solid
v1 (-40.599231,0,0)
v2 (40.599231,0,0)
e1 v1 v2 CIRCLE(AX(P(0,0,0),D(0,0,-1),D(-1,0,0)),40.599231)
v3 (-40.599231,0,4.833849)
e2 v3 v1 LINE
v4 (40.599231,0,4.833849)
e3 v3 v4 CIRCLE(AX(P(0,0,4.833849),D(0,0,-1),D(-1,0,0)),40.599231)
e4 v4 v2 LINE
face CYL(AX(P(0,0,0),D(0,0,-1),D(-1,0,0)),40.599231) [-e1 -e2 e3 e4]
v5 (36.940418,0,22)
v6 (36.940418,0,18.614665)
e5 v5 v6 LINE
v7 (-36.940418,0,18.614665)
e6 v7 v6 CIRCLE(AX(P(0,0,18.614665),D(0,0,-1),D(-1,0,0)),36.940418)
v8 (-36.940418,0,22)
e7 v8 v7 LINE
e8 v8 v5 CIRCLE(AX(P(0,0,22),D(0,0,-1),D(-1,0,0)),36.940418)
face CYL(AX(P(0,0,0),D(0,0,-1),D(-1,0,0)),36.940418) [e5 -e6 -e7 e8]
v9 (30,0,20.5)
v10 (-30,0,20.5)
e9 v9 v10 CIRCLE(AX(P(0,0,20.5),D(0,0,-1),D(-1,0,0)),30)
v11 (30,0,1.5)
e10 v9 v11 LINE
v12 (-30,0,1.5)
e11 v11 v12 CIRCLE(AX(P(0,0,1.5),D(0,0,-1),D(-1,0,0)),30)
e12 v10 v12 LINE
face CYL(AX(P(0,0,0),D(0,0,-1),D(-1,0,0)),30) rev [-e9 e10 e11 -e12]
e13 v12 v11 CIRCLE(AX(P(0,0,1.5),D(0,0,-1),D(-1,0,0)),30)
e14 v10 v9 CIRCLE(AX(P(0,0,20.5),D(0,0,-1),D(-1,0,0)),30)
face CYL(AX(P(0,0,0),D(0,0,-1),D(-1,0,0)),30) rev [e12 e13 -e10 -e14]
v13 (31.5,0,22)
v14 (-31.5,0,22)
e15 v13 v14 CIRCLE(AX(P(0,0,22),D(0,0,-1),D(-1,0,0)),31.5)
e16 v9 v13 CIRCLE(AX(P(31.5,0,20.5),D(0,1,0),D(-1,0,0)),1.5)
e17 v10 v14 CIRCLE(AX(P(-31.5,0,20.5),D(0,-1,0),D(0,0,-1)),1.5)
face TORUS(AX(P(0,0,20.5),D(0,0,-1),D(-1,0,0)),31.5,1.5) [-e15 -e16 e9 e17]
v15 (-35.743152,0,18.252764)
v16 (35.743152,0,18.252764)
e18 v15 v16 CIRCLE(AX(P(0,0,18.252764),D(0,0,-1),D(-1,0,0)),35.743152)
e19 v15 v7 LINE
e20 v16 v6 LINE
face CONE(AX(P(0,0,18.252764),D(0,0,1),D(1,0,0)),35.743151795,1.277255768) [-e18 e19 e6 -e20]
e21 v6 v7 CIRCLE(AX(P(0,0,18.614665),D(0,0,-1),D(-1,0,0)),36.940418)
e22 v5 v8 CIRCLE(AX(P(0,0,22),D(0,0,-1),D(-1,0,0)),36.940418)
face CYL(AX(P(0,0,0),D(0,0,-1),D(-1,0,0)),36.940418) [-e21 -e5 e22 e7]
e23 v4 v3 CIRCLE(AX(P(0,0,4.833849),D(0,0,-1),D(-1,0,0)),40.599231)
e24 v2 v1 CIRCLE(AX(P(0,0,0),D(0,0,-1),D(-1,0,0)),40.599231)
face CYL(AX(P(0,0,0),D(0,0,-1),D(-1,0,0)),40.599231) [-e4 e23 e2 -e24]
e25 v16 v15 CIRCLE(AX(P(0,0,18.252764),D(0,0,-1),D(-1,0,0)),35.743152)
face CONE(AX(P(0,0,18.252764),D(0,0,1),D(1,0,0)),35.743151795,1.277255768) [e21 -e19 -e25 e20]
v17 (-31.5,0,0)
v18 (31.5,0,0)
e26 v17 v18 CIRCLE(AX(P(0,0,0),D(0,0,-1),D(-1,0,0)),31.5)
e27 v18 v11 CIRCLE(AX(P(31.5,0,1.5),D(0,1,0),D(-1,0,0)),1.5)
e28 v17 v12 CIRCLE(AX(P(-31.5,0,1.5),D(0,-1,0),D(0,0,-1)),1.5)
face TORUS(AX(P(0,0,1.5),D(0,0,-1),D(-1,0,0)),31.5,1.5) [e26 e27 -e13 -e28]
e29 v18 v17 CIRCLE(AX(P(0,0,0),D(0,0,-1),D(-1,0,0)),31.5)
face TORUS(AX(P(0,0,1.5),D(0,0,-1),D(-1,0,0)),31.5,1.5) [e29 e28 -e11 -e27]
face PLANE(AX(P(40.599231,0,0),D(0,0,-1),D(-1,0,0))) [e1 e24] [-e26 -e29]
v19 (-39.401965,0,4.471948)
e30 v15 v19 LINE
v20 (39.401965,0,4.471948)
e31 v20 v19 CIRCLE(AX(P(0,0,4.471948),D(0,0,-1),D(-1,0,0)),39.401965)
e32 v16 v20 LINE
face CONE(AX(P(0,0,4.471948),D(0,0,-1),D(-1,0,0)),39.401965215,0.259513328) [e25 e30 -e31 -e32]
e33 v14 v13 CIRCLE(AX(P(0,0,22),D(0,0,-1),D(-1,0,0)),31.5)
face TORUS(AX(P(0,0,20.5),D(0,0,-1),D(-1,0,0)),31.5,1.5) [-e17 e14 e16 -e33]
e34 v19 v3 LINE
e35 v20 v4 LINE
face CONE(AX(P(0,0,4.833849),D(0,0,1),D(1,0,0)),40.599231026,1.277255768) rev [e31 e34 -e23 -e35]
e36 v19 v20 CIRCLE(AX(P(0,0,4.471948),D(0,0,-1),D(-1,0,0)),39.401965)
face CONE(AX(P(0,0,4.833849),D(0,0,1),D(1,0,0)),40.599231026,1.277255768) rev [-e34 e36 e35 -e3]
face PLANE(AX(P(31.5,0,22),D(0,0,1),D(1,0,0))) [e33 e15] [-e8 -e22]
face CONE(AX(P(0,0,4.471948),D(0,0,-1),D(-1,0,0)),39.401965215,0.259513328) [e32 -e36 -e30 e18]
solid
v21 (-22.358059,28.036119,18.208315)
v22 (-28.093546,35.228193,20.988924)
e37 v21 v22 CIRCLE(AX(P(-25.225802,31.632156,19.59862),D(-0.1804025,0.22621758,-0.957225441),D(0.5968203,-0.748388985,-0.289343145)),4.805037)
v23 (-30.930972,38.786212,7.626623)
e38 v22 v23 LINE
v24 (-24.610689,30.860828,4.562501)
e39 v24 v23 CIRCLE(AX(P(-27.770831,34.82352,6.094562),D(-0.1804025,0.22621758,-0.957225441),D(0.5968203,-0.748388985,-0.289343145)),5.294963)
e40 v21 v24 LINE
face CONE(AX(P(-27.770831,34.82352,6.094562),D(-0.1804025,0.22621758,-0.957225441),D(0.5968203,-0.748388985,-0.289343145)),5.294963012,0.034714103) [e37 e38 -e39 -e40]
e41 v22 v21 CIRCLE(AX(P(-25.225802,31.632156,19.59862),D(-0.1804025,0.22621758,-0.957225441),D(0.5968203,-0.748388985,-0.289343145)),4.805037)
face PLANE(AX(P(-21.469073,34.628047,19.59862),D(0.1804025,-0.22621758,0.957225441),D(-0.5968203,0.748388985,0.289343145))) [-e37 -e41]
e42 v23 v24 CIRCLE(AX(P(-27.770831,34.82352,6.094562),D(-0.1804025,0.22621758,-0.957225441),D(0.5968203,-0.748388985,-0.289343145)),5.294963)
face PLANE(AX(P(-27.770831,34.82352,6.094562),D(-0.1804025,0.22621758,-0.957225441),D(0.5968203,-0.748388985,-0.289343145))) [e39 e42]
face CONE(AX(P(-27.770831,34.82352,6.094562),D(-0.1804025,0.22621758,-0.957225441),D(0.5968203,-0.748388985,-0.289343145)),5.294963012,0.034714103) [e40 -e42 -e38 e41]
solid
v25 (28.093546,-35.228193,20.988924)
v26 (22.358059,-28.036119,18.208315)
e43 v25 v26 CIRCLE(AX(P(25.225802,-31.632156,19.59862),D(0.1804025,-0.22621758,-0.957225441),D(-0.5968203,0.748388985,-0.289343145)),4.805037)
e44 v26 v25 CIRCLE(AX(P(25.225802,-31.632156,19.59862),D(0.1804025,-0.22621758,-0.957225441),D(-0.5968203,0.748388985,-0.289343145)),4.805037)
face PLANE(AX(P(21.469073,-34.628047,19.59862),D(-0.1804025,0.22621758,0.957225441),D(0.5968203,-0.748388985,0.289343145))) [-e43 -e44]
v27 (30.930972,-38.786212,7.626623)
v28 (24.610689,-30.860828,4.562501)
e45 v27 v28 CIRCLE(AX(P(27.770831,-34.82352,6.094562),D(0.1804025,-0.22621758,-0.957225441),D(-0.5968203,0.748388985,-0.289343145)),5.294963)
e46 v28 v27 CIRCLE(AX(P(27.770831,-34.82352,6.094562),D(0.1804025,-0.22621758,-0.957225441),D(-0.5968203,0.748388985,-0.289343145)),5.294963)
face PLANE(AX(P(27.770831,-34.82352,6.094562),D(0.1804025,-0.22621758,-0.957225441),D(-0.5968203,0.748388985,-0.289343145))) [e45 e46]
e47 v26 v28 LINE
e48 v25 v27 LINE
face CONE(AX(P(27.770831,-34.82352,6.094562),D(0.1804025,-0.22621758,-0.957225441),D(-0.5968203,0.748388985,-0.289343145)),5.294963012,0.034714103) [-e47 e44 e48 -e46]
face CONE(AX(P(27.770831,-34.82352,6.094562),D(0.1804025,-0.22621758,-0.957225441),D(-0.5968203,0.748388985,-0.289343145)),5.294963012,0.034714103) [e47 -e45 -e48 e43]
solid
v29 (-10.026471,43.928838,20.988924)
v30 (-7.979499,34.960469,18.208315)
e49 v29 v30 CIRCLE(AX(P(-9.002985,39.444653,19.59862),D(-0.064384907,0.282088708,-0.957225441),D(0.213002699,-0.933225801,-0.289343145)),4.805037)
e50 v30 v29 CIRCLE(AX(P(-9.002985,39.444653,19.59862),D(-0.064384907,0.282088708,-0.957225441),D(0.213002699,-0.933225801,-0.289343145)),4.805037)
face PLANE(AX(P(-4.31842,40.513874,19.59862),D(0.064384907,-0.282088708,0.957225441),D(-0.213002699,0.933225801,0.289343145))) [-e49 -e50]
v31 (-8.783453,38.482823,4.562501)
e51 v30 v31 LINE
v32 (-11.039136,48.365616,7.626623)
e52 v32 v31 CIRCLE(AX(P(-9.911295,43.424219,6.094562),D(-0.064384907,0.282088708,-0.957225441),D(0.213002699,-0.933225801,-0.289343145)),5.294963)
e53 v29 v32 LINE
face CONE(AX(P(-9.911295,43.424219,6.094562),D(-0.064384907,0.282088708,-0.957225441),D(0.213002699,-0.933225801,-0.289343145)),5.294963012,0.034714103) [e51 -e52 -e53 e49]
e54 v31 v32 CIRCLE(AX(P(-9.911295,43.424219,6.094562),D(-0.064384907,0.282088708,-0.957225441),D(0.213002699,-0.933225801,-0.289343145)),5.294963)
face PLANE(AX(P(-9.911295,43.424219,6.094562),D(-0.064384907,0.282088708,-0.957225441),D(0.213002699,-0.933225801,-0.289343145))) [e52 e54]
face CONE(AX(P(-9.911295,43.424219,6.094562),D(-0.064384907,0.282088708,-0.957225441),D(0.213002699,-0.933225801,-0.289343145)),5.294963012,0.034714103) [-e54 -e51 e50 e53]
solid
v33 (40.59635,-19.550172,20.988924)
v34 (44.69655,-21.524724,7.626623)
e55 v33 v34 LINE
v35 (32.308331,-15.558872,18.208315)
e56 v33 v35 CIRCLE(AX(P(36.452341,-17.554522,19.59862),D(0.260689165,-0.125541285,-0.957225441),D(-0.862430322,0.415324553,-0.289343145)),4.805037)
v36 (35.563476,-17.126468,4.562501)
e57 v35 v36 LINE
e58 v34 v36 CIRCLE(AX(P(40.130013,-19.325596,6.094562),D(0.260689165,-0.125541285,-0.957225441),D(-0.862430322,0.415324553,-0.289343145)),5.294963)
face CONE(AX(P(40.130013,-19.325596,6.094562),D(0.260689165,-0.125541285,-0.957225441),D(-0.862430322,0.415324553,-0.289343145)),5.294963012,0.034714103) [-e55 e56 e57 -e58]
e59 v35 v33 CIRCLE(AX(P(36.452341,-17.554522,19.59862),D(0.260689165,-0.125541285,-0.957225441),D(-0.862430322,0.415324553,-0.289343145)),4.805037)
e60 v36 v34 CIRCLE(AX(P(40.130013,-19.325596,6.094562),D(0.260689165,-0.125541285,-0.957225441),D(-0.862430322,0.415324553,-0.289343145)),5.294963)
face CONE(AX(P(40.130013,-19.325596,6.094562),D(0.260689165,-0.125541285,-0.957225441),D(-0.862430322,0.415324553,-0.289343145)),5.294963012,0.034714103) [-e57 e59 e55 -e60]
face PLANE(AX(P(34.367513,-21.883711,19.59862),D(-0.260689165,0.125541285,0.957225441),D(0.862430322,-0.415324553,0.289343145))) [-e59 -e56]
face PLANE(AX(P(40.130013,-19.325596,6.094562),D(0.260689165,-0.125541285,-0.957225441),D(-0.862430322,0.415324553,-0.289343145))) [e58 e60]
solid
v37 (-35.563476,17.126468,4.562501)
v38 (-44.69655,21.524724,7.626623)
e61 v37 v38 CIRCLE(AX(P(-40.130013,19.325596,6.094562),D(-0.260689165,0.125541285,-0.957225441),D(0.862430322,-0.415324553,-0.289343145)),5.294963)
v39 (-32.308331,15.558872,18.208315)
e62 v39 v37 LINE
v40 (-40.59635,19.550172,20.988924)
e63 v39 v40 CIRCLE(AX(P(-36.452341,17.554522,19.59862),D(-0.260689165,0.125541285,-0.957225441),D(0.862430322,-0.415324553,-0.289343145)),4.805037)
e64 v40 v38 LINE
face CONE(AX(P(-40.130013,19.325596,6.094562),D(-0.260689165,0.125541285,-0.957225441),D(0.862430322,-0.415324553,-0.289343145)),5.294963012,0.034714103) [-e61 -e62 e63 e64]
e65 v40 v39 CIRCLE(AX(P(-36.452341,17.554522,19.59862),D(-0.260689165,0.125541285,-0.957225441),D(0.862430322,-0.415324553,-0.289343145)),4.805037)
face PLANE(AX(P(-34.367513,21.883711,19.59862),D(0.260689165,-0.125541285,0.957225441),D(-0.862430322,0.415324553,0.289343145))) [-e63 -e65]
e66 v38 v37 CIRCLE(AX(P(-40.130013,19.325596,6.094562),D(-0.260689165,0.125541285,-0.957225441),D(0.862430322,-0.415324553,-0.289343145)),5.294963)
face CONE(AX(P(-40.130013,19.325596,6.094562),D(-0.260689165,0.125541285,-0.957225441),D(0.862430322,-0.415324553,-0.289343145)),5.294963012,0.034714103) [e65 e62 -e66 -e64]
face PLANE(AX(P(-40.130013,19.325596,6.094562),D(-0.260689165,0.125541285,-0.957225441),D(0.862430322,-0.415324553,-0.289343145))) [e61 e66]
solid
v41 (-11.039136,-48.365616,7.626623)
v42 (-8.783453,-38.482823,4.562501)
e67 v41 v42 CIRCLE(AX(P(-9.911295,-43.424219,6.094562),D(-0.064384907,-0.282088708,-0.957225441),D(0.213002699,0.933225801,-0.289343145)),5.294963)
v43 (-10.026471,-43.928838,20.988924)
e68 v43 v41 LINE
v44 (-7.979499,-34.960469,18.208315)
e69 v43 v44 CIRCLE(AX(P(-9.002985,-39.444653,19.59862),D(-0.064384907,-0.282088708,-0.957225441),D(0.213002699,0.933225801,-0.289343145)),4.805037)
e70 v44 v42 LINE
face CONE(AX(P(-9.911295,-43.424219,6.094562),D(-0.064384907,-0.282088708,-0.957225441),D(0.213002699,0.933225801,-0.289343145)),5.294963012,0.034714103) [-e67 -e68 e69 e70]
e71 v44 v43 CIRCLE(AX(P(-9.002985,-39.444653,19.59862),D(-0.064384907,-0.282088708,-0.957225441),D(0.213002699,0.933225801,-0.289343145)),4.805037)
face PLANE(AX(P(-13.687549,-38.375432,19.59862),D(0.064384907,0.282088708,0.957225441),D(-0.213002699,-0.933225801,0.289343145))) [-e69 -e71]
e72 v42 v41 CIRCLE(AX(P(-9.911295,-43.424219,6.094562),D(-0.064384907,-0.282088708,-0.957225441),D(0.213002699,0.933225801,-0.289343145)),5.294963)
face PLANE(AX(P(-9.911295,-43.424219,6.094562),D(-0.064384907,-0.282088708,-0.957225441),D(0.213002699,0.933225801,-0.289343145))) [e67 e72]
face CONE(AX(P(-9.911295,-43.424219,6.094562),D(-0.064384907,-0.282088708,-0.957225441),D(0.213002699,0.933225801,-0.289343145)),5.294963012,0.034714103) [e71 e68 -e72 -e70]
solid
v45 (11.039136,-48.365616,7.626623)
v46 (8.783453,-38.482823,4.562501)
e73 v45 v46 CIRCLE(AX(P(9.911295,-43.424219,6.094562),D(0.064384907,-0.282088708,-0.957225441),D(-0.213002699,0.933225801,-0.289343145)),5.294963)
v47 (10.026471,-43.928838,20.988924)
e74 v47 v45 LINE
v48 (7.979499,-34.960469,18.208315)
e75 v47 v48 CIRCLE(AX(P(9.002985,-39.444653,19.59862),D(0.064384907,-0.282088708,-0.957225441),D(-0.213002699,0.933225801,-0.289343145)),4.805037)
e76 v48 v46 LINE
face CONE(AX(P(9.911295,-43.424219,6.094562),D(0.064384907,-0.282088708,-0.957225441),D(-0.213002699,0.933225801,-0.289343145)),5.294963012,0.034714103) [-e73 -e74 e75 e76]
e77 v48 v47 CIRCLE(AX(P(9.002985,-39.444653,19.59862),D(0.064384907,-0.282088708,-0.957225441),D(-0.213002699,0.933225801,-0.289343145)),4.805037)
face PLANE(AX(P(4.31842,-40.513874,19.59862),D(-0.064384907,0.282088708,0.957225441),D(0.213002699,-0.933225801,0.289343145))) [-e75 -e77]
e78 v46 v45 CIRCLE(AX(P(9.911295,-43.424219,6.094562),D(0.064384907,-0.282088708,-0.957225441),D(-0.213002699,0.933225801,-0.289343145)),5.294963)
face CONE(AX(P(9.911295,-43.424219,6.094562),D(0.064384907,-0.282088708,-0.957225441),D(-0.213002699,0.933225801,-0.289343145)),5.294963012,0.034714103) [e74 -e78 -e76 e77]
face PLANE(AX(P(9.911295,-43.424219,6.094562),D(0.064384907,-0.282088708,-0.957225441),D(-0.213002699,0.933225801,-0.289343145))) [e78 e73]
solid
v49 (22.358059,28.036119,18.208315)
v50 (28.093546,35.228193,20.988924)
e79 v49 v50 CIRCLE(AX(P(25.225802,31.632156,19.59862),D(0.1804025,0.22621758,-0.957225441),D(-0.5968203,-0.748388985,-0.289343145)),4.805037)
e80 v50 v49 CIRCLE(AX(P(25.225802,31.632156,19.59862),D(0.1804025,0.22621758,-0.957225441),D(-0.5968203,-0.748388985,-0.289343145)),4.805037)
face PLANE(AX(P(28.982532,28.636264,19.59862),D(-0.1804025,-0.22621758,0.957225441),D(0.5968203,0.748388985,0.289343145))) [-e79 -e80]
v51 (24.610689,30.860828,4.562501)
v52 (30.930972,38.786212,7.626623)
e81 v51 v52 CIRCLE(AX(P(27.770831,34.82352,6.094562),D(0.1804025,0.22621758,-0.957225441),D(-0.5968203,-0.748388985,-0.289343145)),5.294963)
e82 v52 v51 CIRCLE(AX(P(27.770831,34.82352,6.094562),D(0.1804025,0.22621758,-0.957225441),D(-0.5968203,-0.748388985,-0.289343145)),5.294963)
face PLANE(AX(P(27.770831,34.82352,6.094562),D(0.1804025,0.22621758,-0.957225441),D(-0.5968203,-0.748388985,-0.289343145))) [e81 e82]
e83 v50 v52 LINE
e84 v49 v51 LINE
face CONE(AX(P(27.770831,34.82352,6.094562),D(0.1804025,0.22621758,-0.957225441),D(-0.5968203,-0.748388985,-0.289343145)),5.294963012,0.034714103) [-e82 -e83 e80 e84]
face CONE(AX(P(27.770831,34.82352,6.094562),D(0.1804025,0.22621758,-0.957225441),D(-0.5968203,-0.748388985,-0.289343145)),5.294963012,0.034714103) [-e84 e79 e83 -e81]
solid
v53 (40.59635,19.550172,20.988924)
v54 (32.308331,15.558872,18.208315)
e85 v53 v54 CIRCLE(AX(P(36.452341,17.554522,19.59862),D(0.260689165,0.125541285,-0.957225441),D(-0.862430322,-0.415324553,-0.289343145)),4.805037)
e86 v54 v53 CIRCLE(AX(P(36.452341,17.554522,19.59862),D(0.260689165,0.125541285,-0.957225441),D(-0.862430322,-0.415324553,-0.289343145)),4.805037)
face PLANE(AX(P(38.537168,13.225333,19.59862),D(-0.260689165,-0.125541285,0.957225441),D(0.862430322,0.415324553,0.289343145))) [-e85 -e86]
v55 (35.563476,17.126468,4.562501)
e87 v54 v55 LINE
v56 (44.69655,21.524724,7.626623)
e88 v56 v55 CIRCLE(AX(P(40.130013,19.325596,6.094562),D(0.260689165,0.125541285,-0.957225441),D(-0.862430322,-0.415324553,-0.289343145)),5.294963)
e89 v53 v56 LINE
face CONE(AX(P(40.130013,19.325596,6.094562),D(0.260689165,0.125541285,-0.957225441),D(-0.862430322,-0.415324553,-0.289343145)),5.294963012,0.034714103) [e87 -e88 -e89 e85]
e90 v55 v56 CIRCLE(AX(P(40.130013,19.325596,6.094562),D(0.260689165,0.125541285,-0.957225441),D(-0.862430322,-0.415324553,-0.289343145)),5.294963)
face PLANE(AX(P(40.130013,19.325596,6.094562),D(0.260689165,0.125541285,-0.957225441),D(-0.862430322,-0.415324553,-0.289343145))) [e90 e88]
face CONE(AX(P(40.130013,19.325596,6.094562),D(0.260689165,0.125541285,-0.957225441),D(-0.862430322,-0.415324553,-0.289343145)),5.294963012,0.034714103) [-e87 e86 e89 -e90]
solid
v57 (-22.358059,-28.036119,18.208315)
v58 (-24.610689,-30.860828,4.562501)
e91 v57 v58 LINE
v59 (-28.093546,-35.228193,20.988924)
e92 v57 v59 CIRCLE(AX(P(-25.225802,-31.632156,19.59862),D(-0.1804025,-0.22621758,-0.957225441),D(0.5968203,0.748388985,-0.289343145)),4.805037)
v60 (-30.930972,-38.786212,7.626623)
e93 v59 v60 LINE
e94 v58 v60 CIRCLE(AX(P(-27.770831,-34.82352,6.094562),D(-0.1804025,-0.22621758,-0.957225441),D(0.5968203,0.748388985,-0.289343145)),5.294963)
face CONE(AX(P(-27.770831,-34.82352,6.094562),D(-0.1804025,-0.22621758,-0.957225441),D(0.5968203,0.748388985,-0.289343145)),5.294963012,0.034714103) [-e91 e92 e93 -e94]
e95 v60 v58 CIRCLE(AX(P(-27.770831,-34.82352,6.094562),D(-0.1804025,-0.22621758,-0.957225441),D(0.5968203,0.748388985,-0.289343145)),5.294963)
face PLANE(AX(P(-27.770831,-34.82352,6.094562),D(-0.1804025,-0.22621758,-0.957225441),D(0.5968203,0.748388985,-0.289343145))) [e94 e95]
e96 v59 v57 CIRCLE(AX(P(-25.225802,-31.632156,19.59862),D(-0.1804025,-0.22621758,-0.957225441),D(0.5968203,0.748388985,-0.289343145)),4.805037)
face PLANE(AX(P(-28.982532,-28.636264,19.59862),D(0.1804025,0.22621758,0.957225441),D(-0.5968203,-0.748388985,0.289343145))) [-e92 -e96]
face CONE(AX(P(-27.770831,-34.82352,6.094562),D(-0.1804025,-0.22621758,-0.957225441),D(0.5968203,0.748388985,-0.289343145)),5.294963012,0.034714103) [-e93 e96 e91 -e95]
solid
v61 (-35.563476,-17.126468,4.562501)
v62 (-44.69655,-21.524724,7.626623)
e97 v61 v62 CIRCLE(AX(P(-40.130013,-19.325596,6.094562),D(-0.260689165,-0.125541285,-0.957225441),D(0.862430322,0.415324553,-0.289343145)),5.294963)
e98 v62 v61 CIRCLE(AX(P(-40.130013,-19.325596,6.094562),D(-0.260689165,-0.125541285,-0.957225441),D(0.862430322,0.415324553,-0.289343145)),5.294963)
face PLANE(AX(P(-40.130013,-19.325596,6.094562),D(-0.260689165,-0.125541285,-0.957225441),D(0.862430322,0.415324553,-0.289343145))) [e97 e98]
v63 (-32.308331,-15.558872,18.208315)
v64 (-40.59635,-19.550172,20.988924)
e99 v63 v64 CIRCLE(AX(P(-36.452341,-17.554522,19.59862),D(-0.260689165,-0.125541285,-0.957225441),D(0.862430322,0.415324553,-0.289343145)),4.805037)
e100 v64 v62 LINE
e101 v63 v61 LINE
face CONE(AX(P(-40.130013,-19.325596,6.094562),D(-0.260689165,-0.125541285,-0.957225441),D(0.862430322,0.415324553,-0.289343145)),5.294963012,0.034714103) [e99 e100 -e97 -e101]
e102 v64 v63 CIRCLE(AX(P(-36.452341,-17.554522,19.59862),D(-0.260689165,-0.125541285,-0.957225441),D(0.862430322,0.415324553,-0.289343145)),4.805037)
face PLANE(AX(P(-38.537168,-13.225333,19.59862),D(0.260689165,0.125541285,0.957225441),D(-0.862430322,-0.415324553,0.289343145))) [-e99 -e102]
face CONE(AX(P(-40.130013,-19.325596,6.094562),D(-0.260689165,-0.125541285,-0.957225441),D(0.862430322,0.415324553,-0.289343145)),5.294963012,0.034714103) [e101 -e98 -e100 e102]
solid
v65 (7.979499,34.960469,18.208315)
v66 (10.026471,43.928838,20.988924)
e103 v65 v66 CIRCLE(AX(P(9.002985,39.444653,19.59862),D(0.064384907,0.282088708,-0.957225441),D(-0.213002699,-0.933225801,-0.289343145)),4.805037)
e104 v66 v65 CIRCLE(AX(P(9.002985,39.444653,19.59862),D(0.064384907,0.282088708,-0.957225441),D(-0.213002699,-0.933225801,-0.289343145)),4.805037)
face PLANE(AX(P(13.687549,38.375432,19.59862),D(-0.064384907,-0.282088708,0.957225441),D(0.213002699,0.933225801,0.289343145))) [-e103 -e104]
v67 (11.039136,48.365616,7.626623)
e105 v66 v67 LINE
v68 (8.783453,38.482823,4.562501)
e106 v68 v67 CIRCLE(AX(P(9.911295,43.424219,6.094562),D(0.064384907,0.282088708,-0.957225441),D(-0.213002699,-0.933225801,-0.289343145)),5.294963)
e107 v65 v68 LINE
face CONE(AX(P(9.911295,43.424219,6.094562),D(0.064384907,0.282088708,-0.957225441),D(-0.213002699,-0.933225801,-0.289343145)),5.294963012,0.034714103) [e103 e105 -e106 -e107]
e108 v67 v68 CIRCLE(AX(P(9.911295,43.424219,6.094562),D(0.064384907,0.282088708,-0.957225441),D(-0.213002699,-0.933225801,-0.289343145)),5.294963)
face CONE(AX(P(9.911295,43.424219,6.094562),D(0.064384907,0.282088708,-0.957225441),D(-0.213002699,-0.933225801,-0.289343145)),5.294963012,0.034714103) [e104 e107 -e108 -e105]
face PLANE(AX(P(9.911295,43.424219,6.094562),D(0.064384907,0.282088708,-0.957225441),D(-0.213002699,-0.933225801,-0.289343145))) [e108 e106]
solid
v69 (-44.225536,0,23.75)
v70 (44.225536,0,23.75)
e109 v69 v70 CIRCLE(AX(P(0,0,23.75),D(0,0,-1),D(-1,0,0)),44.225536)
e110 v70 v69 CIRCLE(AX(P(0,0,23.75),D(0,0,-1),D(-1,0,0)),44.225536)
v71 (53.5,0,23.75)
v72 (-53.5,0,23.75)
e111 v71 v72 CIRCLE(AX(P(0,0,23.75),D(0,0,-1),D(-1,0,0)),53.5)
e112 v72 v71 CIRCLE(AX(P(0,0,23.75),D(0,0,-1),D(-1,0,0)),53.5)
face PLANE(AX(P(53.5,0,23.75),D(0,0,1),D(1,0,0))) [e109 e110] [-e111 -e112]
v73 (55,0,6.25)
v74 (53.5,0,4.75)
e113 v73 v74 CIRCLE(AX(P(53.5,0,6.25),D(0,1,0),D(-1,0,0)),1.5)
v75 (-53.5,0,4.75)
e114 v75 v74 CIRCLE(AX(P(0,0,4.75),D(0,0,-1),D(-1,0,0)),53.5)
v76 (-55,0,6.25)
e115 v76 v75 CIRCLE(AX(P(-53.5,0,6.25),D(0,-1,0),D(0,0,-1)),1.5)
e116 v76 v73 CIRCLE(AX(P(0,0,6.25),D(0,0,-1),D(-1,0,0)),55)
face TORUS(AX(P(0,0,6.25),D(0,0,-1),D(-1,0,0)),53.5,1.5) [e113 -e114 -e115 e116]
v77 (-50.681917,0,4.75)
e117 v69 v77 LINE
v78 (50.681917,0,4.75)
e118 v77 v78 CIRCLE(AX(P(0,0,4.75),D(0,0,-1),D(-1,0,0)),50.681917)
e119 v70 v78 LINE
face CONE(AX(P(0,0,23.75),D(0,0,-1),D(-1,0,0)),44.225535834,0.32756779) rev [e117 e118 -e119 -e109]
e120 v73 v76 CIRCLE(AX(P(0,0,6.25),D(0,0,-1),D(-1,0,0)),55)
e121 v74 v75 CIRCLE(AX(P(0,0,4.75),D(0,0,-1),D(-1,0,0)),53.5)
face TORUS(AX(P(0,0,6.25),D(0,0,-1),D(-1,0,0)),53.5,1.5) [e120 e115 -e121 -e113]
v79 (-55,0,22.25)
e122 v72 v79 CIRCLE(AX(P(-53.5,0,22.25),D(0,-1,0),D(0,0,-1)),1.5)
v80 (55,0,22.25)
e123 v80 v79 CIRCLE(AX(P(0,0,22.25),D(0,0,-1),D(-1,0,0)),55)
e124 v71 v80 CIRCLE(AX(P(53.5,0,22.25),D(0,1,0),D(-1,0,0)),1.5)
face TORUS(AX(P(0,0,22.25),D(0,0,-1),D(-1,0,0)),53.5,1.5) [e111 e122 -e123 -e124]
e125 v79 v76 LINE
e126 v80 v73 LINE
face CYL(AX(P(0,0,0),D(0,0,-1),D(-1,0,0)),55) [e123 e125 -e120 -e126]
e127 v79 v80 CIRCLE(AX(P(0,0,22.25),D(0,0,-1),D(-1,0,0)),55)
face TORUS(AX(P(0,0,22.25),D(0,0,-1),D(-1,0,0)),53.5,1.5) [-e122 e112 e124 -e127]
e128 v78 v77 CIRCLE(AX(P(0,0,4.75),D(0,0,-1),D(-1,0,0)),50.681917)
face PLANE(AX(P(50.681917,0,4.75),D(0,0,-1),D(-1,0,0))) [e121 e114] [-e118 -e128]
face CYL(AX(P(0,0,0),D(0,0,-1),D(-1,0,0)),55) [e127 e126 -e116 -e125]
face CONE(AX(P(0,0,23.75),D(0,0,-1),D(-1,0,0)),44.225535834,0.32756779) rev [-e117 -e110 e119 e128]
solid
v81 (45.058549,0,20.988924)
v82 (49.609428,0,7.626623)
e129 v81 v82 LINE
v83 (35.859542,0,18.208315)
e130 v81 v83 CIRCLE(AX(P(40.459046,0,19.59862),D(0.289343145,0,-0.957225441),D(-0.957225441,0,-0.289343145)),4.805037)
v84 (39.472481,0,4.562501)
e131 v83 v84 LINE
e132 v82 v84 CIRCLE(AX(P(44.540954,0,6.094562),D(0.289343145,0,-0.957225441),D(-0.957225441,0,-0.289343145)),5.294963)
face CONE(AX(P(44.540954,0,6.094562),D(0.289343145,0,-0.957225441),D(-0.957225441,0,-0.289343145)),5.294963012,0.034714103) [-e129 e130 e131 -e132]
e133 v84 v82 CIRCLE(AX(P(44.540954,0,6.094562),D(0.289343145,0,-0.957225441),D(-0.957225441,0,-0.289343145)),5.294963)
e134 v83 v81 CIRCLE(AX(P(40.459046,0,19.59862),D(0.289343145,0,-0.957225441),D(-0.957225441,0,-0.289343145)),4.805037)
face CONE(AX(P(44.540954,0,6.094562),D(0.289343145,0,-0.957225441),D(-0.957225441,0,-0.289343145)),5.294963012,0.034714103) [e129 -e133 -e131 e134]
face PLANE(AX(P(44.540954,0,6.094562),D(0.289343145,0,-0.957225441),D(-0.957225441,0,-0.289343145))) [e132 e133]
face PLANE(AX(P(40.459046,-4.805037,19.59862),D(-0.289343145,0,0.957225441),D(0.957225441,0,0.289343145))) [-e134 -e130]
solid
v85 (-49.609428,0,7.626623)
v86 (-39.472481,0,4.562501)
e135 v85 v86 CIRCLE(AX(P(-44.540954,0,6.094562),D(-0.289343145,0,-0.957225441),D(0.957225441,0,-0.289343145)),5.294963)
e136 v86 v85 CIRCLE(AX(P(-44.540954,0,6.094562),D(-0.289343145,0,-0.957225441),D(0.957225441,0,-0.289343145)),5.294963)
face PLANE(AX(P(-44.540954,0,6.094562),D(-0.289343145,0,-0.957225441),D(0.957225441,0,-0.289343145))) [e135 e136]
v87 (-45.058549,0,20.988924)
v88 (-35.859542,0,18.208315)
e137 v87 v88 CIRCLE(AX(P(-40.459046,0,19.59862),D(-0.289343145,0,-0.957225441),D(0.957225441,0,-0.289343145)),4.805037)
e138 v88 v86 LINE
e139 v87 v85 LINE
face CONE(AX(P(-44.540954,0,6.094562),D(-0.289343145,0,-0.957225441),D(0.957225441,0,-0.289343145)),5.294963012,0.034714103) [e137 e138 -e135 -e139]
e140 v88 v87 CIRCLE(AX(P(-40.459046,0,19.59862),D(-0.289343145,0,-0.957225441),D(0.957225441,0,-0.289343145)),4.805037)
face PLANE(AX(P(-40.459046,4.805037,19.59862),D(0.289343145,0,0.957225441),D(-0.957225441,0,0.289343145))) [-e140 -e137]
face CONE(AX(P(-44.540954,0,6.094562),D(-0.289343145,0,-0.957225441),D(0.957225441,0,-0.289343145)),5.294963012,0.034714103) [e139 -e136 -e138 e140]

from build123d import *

# Parameters (mm, degrees)
PATTERN_CIRCULAR_1_COUNT = 14


with BuildPart() as part:
    # 草图1 → 旋转1 (revolve)
    with BuildSketch(Plane.XZ, mode=Mode.PRIVATE) as revolve_1_sk:
        with BuildLine():
            Line((40.599231026, 0), (31.5, 0))
            ThreePointArc((31.5, 0), (30.439339828, 0.439339828), (30, 1.5))
            Line((30, 1.5), (30, 20.5))
            ThreePointArc((30, 20.5), (30.439339828, 21.560660172), (31.5, 22))
            Line((31.5, 22), (36.940417606, 22))
            Line((36.940417606, 22), (36.940417606, 18.614664842))
            Line((36.940417606, 18.614664842), (35.743151795, 18.25276404))
            Line((35.743151795, 18.25276404), (39.401965215, 4.471948303))
            Line((39.401965215, 4.471948303), (40.599231026, 4.833849105))
            Line((40.599231026, 4.833849105), (40.599231026, 0))
        make_face()
    revolve(revolve_1_sk.sketch.rotate(Axis((0, 0, 0), (0, 0, 1)), 180), axis=Axis((0, 0, 0), (0, 0, 1)))


with BuildPart() as body_2:
    # 草图2 → 旋转2 (revolve)
    with BuildSketch(Plane(origin=(42.5, 0, 12.846590909), x_dir=(0, -1, 0), z_dir=(-0.9572254408742195, 0, -0.28934314462789035)), mode=Mode.PRIVATE) as revolve_2_sk:
        Polygon((0, -7.05375), (5.294963012, -7.05375), (4.805036988, 7.05375), (0, 7.05375), align=None)
    revolve(revolve_2_sk.sketch.rotate(Axis((42.5, 0, 12.846590909), (-0.2893431446278901, 0, 0.9572254408742195)), 270), axis=Axis((42.5, 0, 12.846590909), (-0.2893431446278901, 0, 0.9572254408742195)))


with BuildPart() as body_3:
    # 草图3 → 旋转3 (revolve)
    with BuildSketch(Plane.XZ, mode=Mode.PRIVATE) as revolve_3_sk:
        with BuildLine():
            Line((50.681917458, 4.75), (53.499999996, 4.75))
            ThreePointArc((53.499999996, 4.75), (54.560660168, 5.189339828), (54.999999996, 6.25))
            Line((54.999999996, 6.25), (54.999999996, 22.25))
            ThreePointArc((54.999999996, 22.25), (54.560660168, 23.310660172), (53.499999996, 23.75))
            Line((53.499999996, 23.75), (44.225535831, 23.75))
            Line((44.225535831, 23.75), (50.681917458, 4.75))
        make_face()
    revolve(revolve_3_sk.sketch.rotate(Axis((-4e-09, 0, 0), (0, 0, 1)), 180), axis=Axis((-4e-09, 0, 0), (0, 0, 1)))


with BuildPart() as pattern_circular_1_1:
    # 阵列(圆周)1: pattern copy
    add(body_2.part.rotate(Axis((0, 0, 0), (0, 0, 1)), 1 * 360 / PATTERN_CIRCULAR_1_COUNT))


with BuildPart() as pattern_circular_1_2:
    # 阵列(圆周)1: pattern copy
    add(body_2.part.rotate(Axis((0, 0, 0), (0, 0, 1)), 2 * 360 / PATTERN_CIRCULAR_1_COUNT))


with BuildPart() as pattern_circular_1_3:
    # 阵列(圆周)1: pattern copy
    add(body_2.part.rotate(Axis((0, 0, 0), (0, 0, 1)), 3 * 360 / PATTERN_CIRCULAR_1_COUNT))


with BuildPart() as pattern_circular_1_4:
    # 阵列(圆周)1: pattern copy
    add(body_2.part.rotate(Axis((0, 0, 0), (0, 0, 1)), 4 * 360 / PATTERN_CIRCULAR_1_COUNT))


with BuildPart() as pattern_circular_1_5:
    # 阵列(圆周)1: pattern copy
    add(body_2.part.rotate(Axis((0, 0, 0), (0, 0, 1)), 5 * 360 / PATTERN_CIRCULAR_1_COUNT))


with BuildPart() as pattern_circular_1_6:
    # 阵列(圆周)1: pattern copy
    add(body_2.part.rotate(Axis((0, 0, 0), (0, 0, 1)), 6 * 360 / PATTERN_CIRCULAR_1_COUNT))


with BuildPart() as pattern_circular_1_7:
    # 阵列(圆周)1: pattern copy
    add(body_2.part.rotate(Axis((0, 0, 0), (0, 0, 1)), 7 * 360 / PATTERN_CIRCULAR_1_COUNT))


with BuildPart() as pattern_circular_1_8:
    # 阵列(圆周)1: pattern copy
    add(body_2.part.rotate(Axis((0, 0, 0), (0, 0, 1)), 8 * 360 / PATTERN_CIRCULAR_1_COUNT))


with BuildPart() as pattern_circular_1_9:
    # 阵列(圆周)1: pattern copy
    add(body_2.part.rotate(Axis((0, 0, 0), (0, 0, 1)), 9 * 360 / PATTERN_CIRCULAR_1_COUNT))


with BuildPart() as pattern_circular_1_10:
    # 阵列(圆周)1: pattern copy
    add(body_2.part.rotate(Axis((0, 0, 0), (0, 0, 1)), 10 * 360 / PATTERN_CIRCULAR_1_COUNT))


with BuildPart() as pattern_circular_1_11:
    # 阵列(圆周)1: pattern copy
    add(body_2.part.rotate(Axis((0, 0, 0), (0, 0, 1)), 11 * 360 / PATTERN_CIRCULAR_1_COUNT))


with BuildPart() as pattern_circular_1_12:
    # 阵列(圆周)1: pattern copy
    add(body_2.part.rotate(Axis((0, 0, 0), (0, 0, 1)), 12 * 360 / PATTERN_CIRCULAR_1_COUNT))


with BuildPart() as pattern_circular_1_13:
    # 阵列(圆周)1: pattern copy
    add(body_2.part.rotate(Axis((0, 0, 0), (0, 0, 1)), 13 * 360 / PATTERN_CIRCULAR_1_COUNT))


solid = Compound([part.part, body_2.part, body_3.part, pattern_circular_1_1.part, pattern_circular_1_2.part, pattern_circular_1_3.part, pattern_circular_1_4.part, pattern_circular_1_5.part, pattern_circular_1_6.part, pattern_circular_1_7.part, pattern_circular_1_8.part, pattern_circular_1_9.part, pattern_circular_1_10.part, pattern_circular_1_11.part, pattern_circular_1_12.part, pattern_circular_1_13.part])
